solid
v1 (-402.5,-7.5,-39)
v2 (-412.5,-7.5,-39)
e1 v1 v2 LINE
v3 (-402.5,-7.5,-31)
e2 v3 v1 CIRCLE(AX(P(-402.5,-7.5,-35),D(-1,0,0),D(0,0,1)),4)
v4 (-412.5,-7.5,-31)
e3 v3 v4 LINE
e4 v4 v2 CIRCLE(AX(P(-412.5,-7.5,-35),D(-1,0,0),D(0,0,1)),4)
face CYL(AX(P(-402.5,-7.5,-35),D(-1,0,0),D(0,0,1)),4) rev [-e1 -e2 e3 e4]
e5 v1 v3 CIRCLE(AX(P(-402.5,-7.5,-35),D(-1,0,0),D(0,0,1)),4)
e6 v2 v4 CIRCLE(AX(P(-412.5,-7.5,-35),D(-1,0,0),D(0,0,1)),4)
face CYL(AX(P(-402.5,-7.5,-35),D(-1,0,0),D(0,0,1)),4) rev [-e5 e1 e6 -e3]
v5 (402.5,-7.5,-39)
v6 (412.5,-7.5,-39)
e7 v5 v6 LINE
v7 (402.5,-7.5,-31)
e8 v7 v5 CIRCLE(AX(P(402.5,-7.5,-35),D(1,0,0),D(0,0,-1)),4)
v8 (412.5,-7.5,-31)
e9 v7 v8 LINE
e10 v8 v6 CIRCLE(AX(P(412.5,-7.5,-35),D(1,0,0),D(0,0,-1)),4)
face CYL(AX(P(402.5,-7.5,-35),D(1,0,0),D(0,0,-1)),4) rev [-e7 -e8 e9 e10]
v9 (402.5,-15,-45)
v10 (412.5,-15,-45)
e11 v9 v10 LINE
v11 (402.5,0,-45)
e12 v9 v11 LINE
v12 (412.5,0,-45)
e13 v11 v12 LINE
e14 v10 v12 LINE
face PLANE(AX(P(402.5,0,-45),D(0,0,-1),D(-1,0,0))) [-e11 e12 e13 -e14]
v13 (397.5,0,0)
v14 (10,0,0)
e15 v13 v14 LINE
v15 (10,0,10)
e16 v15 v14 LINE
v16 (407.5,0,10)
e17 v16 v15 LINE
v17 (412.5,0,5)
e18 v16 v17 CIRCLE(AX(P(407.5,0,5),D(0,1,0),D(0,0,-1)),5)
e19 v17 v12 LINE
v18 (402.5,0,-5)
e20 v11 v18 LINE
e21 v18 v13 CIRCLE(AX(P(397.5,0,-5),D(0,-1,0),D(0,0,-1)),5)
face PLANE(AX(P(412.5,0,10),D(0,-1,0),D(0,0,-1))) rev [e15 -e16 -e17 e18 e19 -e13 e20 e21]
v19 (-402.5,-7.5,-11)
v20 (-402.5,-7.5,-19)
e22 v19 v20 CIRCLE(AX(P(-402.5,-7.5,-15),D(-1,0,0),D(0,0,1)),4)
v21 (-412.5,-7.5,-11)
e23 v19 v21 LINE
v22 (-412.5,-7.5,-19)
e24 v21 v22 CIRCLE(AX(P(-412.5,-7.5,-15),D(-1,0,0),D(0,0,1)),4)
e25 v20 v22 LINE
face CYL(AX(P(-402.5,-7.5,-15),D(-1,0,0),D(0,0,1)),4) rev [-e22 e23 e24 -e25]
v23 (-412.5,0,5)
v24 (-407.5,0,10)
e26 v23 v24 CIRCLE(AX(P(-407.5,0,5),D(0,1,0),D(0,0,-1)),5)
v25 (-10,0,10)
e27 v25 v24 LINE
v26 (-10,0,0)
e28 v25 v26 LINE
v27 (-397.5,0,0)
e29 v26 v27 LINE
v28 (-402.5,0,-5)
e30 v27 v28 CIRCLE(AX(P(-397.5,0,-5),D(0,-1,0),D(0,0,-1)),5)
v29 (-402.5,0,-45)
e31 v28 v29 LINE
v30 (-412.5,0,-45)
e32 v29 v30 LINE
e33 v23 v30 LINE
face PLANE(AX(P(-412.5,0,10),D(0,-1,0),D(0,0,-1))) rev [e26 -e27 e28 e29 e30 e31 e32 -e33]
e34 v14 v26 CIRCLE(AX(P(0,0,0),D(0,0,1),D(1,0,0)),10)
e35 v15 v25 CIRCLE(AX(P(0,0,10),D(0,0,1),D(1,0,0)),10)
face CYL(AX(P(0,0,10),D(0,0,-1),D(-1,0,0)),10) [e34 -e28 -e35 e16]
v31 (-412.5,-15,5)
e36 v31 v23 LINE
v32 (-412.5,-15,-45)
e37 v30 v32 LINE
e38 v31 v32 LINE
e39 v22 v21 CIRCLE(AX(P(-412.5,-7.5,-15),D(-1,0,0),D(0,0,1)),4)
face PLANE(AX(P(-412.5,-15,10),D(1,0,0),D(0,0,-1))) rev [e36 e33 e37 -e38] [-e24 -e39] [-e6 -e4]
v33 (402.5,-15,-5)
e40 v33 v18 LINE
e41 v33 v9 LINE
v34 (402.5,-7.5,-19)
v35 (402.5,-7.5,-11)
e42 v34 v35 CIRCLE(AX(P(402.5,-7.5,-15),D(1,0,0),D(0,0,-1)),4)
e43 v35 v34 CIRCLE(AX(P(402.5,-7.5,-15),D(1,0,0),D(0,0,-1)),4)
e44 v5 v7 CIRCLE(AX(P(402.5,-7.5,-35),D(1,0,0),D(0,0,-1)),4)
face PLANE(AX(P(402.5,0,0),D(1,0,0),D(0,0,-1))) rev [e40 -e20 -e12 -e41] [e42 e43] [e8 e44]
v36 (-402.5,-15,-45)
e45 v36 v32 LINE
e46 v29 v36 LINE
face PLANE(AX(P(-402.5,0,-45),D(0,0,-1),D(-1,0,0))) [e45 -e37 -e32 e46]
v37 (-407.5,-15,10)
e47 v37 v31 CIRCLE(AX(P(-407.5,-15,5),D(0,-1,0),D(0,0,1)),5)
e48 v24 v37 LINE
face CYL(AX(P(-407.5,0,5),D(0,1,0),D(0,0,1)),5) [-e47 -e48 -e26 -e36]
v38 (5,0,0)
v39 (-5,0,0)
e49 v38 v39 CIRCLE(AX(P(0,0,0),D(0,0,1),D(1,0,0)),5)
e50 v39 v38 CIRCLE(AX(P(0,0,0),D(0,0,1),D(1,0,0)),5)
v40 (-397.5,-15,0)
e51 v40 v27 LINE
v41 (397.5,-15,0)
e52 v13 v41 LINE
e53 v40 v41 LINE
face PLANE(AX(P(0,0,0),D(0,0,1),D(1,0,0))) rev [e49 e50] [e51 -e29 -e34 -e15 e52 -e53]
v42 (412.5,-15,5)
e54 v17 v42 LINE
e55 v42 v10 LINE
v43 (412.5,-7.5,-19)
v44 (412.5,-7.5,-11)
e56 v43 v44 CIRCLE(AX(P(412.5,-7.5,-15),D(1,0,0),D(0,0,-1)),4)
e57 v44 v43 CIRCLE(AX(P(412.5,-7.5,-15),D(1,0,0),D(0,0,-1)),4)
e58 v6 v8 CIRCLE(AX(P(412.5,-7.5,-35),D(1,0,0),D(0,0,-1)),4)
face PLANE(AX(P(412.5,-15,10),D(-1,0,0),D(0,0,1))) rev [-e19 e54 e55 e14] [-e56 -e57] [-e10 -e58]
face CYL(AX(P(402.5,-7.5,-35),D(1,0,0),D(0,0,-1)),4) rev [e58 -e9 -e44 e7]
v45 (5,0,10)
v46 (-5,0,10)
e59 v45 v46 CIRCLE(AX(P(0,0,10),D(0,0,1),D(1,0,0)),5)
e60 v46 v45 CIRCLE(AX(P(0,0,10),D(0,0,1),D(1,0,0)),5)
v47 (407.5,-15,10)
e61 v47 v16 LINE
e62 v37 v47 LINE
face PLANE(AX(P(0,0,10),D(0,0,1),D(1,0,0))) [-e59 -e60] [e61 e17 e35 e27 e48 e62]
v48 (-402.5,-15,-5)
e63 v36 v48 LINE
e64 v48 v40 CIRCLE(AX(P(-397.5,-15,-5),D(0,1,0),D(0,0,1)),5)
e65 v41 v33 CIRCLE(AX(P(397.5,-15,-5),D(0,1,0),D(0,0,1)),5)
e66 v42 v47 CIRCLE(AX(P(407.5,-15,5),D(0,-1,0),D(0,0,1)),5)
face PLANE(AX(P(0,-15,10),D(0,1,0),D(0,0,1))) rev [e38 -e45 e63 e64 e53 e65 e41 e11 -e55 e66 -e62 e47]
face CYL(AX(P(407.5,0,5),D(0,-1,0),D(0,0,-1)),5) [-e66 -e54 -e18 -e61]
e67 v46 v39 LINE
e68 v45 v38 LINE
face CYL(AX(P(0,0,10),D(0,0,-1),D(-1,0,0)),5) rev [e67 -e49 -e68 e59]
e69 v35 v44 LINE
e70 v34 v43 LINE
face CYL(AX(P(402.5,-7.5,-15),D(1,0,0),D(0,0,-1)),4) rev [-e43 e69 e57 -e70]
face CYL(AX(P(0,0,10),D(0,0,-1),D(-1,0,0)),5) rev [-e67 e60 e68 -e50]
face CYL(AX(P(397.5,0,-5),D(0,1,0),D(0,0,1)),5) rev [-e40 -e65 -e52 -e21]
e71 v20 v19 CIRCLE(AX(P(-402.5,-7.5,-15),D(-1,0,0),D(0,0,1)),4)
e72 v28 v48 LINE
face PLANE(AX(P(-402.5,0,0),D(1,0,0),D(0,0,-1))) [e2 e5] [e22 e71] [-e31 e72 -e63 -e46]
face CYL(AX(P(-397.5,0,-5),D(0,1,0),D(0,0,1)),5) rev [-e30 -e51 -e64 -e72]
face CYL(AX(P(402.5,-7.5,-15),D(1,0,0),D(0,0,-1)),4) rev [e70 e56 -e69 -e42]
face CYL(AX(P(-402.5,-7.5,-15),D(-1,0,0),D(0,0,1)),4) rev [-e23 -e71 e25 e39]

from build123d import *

# Parameters (mm, degrees)
SKETCH_1_R      = 5
EXTRUDE_1_DEPTH = 10
SKETCH_2_W      = 45
SKETCH_2_H      = 15
SKETCH_2_R      = 4
EXTRUDE_2_DEPTH = 10
EXTRUDE_START   = -10
SKETCH_3_W      = 45
SKETCH_3_H      = 15
SKETCH_3_R      = 4
EXTRUDE_3_DEPTH = 10
FILLET_1_R      = 5


with BuildPart() as part:
    # 草图1 → 凸台-拉伸1 (new body)
    with BuildSketch(Plane.XY):
        with BuildLine():
            Line((0, -15), (412.5, -15))
            Line((412.5, -15), (412.5, 0))
            Line((412.5, 0), (10, 0))
            ThreePointArc((10, 0), (0, 10), (-10, 0))
            Line((-10, 0), (-412.5, 0))
            Line((-412.5, 0), (-412.5, -15))
            Line((-412.5, -15), (0, -15))
        make_face()
        Circle(SKETCH_1_R, mode=Mode.SUBTRACT)
    extrude(amount=EXTRUDE_1_DEPTH)

    # 草图2 → 凸台-拉伸2 (add)
    with BuildSketch(Plane(origin=(412.5, 0, 0), x_dir=(0, 0, -1), z_dir=(1, 0, 0))):
        with Locations((22.5, -7.5)):
            Rectangle(SKETCH_2_W, SKETCH_2_H)
        with Locations((15, -7.5)):
            Circle(SKETCH_2_R, mode=Mode.SUBTRACT)
        with Locations((35, -7.5)):
            Circle(SKETCH_2_R, mode=Mode.SUBTRACT)
    extrude(amount=-EXTRUDE_2_DEPTH)

    # 草图3 → 凸台-拉伸3 (add)
    with BuildSketch(Plane.ZY.offset(412.5).offset(EXTRUDE_START)):
        with Locations((-22.5, -7.5)):
            Rectangle(SKETCH_3_W, SKETCH_3_H)
        with Locations(Location((-35, -7.5, 0), (0, 0, 180))):
            Circle(SKETCH_3_R, mode=Mode.SUBTRACT)
        with Locations(Location((-15, -7.5, 0), (0, 0, 180))):
            Circle(SKETCH_3_R, mode=Mode.SUBTRACT)
    extrude(amount=EXTRUDE_3_DEPTH)

    # 圆角1
    fillet_1_edges = [part.edges().sort_by_distance(p)[0] for p in [
        (-412.5, -7.5, 10),
        (402.5, -7.5, 0),
        (412.5, -7.5, 10),
        (-402.5, -7.5, 0),
    ]]
    fillet(fillet_1_edges, radius=FILLET_1_R)


solid = part.part
